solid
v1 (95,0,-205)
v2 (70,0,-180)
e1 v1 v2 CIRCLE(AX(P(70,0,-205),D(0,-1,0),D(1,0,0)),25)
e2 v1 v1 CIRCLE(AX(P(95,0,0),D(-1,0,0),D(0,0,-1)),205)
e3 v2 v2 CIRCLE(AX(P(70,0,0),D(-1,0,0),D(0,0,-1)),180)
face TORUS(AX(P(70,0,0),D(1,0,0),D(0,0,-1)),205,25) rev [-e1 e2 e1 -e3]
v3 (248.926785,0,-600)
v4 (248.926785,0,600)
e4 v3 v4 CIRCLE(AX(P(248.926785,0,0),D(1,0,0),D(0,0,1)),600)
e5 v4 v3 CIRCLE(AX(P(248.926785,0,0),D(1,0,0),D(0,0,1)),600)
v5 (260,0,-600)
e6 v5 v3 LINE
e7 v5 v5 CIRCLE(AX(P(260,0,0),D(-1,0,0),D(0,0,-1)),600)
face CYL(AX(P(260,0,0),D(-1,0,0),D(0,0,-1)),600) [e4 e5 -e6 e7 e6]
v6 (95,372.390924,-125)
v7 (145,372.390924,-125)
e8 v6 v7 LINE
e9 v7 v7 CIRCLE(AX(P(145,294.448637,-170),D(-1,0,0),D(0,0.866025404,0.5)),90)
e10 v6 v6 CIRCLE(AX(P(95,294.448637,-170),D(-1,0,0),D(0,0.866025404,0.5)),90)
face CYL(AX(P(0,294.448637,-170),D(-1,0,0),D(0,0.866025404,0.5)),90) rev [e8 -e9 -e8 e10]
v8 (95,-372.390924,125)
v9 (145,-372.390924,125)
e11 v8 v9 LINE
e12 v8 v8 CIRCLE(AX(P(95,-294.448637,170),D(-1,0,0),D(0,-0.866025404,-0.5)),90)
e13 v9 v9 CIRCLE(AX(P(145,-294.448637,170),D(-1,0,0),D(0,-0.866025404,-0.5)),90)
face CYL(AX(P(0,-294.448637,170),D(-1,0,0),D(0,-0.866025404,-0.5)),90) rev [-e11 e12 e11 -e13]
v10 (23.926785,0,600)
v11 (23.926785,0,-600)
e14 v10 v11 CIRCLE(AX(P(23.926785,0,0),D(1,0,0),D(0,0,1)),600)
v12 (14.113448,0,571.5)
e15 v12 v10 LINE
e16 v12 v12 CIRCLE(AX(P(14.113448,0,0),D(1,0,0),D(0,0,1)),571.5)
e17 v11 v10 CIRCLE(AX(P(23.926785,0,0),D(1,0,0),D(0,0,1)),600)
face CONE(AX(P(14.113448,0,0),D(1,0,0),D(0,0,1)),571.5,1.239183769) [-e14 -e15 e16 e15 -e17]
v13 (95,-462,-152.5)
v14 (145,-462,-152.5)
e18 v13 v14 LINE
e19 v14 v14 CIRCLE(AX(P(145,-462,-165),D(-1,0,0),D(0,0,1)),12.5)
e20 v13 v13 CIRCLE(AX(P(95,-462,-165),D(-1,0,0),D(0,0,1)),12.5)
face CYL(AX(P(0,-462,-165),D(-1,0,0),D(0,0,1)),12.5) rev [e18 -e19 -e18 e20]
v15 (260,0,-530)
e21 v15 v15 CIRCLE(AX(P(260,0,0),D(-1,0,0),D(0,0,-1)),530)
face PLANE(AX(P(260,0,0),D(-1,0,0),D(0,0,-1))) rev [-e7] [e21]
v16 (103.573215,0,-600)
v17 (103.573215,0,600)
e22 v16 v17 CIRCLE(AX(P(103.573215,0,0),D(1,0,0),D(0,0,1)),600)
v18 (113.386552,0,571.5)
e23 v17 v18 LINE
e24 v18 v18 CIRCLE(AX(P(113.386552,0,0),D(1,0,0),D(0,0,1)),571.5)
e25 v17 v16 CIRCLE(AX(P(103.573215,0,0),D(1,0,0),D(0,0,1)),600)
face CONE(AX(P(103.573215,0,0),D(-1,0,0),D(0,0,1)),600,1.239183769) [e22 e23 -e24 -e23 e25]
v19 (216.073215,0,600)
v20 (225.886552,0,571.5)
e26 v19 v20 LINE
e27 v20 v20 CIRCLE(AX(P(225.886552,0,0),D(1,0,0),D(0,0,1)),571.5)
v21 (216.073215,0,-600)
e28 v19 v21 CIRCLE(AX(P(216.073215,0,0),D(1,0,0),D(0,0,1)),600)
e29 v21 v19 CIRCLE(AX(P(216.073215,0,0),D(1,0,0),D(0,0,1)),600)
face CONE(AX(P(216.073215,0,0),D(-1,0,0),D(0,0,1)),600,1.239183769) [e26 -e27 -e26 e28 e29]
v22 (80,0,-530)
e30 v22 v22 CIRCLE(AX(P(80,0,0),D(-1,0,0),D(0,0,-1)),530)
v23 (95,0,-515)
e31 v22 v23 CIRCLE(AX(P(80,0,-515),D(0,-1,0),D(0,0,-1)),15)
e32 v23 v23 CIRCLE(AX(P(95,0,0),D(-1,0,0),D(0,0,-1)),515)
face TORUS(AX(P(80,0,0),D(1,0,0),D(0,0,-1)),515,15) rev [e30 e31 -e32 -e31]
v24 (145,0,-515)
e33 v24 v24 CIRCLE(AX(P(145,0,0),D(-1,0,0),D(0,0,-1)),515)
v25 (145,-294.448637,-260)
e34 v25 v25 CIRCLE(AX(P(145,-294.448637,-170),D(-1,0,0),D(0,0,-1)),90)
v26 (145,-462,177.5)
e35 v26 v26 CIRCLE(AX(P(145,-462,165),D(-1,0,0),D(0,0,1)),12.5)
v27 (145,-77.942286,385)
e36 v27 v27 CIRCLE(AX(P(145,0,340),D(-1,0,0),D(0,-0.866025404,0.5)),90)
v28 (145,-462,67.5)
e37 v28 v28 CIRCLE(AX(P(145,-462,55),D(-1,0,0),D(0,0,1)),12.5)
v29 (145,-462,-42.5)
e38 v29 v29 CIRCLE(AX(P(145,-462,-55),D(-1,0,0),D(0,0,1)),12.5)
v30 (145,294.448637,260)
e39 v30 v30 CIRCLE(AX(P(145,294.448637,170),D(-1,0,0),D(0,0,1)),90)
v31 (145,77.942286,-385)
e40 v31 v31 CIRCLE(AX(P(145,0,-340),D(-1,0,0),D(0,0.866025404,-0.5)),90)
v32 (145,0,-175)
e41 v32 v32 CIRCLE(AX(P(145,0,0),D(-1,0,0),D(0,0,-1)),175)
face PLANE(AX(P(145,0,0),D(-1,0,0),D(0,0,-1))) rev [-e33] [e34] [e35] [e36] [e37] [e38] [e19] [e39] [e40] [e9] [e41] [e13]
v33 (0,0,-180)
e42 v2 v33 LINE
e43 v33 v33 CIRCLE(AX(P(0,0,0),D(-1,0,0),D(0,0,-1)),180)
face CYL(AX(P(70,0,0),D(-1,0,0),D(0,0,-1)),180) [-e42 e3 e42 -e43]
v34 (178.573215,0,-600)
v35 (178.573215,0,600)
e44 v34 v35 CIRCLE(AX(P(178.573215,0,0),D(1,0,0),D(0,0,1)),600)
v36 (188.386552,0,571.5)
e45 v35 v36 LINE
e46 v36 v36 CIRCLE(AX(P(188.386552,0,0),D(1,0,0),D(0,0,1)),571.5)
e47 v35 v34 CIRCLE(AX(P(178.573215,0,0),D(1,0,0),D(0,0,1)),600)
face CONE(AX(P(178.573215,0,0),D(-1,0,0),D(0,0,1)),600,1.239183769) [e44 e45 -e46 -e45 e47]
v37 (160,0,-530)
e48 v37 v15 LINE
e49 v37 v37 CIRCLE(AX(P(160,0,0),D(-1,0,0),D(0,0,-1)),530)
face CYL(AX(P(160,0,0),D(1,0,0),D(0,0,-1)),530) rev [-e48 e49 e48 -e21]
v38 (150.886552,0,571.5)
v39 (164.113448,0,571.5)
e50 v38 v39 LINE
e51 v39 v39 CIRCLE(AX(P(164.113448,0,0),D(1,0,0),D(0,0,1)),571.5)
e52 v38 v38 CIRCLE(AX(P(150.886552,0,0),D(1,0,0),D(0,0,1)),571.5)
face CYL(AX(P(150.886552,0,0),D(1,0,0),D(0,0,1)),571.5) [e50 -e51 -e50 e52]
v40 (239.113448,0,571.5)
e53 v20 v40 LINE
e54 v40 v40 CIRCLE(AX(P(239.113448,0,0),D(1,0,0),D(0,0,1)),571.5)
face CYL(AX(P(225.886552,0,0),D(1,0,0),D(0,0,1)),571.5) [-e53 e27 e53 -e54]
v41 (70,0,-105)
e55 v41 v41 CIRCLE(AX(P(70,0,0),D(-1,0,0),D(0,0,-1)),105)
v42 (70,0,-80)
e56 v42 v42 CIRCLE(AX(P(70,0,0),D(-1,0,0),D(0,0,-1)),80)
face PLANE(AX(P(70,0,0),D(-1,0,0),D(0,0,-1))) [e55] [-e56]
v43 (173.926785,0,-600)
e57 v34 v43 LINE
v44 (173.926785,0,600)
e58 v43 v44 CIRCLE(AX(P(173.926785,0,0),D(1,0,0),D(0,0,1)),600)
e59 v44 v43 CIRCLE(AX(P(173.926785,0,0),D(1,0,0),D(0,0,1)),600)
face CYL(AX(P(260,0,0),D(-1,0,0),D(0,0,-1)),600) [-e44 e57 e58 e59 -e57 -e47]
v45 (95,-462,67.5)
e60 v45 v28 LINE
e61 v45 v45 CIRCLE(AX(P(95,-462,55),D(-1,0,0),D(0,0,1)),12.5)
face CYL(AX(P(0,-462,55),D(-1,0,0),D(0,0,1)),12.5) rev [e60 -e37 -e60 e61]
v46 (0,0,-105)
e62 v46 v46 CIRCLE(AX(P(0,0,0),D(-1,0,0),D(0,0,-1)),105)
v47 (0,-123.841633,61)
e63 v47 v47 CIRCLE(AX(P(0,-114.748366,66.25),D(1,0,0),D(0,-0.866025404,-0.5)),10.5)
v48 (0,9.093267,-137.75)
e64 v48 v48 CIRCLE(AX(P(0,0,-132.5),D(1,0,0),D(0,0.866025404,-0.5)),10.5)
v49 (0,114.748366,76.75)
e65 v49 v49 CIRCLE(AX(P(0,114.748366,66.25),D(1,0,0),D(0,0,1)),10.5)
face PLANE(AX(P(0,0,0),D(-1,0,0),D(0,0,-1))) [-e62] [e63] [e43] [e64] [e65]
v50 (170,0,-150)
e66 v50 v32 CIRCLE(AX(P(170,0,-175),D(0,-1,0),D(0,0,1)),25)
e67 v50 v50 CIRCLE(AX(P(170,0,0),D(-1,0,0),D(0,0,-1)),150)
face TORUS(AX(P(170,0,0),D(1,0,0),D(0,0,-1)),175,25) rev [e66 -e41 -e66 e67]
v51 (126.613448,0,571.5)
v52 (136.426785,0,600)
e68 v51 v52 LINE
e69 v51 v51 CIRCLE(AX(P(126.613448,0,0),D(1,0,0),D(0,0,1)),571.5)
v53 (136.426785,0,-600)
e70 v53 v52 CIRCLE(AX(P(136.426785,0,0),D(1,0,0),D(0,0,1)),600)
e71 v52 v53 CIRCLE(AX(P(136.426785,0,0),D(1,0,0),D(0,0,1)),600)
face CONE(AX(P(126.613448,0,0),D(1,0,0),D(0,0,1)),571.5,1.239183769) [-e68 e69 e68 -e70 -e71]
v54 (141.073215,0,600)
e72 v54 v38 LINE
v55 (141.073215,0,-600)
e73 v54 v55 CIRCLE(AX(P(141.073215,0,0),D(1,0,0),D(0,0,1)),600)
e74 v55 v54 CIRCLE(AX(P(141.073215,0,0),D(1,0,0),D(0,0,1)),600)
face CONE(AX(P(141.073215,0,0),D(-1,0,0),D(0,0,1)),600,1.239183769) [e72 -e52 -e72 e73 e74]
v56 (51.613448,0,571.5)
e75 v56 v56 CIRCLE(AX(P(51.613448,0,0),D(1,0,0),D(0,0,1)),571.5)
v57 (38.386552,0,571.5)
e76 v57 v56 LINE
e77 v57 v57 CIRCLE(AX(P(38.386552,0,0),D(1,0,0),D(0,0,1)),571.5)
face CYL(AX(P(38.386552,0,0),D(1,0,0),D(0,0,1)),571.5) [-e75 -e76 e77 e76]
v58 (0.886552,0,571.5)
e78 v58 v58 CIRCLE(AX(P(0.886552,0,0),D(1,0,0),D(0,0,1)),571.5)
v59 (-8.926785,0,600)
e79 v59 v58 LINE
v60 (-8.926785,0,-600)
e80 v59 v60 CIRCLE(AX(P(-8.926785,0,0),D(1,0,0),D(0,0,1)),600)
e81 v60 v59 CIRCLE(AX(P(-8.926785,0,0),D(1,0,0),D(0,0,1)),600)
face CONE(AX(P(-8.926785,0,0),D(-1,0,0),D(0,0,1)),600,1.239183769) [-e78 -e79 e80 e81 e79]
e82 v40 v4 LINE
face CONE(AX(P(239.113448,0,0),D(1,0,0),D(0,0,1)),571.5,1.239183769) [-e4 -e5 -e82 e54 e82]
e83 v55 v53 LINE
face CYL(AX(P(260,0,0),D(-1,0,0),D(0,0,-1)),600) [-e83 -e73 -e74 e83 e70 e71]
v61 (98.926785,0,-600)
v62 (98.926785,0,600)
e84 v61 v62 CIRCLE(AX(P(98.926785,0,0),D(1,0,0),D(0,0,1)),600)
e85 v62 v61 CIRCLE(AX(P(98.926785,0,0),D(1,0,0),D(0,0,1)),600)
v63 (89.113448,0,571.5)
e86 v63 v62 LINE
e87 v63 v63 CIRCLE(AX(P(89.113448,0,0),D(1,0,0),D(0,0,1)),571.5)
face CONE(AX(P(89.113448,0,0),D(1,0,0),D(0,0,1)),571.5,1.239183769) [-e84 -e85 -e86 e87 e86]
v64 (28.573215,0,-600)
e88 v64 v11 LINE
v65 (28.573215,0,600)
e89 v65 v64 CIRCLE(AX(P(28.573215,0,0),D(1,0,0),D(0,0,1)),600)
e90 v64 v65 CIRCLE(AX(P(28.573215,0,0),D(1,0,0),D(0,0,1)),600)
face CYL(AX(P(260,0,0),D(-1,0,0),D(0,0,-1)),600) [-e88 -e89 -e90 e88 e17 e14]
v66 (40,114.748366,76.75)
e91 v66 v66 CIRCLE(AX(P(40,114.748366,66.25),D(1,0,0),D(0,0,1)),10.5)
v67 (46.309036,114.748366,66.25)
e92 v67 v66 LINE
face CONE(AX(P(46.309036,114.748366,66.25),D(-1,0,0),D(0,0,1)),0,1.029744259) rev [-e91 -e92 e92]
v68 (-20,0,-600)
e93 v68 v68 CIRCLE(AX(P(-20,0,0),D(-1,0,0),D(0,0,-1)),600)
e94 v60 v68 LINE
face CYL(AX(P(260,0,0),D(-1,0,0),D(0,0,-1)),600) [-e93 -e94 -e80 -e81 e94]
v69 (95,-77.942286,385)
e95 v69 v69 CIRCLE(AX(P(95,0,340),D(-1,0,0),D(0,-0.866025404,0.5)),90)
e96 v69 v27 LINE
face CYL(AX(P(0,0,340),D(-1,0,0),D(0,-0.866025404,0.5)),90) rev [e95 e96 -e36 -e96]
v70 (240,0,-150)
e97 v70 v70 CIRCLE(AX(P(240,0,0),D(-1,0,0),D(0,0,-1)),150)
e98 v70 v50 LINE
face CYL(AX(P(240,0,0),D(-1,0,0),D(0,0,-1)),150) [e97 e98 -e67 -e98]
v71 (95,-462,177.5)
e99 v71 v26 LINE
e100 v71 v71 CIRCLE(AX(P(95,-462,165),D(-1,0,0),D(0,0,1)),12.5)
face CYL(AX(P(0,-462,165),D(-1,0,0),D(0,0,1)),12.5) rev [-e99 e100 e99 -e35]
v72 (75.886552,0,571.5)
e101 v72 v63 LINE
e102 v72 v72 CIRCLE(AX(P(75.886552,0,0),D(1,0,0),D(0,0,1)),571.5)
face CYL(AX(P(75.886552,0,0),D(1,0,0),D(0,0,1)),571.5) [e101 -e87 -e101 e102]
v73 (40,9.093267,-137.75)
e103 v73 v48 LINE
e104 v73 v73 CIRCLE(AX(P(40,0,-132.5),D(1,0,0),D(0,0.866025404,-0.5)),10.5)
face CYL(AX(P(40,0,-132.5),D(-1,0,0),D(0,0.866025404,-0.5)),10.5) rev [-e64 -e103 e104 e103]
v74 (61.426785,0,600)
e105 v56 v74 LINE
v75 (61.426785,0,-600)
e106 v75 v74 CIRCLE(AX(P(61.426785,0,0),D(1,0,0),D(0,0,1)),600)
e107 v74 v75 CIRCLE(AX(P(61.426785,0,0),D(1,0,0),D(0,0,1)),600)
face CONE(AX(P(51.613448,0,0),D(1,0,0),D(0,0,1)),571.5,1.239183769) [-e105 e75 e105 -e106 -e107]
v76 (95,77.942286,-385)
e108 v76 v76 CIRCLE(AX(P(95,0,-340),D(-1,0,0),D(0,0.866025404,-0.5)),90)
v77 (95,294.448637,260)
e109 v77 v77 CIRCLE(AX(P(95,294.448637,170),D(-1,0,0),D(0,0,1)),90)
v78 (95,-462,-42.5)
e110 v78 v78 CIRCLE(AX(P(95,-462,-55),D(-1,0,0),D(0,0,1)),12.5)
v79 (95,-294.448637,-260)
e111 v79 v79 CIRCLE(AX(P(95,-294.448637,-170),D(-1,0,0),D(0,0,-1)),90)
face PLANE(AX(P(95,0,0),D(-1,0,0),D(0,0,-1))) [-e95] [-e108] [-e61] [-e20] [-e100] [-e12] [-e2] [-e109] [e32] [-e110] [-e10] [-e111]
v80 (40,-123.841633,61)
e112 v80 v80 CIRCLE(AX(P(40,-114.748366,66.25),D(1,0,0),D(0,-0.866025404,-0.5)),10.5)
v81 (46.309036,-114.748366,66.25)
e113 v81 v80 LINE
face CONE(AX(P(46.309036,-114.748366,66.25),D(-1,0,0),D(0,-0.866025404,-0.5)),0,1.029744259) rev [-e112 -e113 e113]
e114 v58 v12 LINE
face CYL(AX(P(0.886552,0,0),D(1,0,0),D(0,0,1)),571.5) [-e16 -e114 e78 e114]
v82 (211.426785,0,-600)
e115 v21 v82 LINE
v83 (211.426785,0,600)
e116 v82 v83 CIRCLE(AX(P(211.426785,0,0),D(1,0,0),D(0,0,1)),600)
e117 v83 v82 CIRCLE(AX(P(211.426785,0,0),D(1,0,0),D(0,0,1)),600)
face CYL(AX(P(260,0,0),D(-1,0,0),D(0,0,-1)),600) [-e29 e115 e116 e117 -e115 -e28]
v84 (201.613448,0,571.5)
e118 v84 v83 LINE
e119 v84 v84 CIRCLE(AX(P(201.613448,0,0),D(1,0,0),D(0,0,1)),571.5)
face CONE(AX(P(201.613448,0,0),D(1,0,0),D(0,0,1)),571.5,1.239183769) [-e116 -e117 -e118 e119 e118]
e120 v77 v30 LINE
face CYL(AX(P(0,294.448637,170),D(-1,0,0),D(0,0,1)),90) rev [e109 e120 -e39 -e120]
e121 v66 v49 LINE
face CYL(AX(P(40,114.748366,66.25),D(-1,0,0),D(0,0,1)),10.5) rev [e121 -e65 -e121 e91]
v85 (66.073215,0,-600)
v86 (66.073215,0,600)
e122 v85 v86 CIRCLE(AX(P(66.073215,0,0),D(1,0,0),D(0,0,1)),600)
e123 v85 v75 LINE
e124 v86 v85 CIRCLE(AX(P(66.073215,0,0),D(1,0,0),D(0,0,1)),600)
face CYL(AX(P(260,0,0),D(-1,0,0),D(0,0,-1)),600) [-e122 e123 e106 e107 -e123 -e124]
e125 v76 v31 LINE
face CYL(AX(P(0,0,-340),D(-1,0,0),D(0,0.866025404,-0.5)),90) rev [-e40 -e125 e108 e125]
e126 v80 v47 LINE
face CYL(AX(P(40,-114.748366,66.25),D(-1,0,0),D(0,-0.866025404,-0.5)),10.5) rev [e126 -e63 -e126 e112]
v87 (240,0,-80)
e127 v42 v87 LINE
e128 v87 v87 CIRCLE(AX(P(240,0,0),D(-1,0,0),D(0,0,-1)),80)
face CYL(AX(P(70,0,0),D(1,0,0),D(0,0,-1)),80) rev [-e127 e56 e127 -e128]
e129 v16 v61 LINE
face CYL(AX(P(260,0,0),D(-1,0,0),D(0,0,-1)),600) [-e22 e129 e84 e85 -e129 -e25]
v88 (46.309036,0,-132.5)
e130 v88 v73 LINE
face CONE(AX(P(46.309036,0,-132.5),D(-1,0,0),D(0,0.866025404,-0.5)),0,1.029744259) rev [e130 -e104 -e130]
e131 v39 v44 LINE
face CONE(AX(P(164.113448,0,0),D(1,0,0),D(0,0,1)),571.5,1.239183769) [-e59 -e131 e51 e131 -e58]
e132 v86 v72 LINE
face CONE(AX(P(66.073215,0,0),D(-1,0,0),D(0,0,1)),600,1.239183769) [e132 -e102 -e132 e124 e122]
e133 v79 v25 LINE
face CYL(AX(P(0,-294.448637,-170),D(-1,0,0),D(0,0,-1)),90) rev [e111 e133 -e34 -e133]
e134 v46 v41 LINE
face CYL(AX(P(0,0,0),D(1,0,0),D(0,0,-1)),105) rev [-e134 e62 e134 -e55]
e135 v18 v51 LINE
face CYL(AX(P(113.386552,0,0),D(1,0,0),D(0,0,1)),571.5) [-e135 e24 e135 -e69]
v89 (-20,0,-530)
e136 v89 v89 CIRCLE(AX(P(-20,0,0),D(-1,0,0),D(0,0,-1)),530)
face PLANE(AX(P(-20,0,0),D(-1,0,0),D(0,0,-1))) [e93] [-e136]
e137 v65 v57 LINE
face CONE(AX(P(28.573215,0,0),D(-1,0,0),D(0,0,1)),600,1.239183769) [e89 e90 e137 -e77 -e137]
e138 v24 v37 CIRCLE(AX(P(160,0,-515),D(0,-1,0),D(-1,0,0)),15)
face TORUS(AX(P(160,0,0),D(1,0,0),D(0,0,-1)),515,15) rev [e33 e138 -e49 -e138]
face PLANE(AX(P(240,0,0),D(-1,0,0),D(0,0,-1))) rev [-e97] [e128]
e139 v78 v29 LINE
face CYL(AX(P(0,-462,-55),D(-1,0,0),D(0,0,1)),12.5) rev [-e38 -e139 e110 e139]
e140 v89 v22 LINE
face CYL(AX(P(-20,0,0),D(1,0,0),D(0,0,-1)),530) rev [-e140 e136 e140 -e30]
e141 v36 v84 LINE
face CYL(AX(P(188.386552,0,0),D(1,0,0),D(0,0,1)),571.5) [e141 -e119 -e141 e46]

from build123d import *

# Parameters (mm, degrees)
SKETCH4_R          = 90
CUT_EXTRUDE1_DEPTH = 343
CIRPATTERN1_COUNT  = 6
CIRPATTERN2_COUNT  = 3
SKETCH8_R          = 12.5
CUT_EXTRUDE3_DEPTH = 238
LPATTERN1_COUNT    = 7
LPATTERN1_PITCH    = 37.5


with BuildPart() as part:
    # Sketch2 → Revolve1 (revolve)
    with BuildSketch(Plane.XY, mode=Mode.PRIVATE) as revolve1_sk:
        with BuildLine():
            Line((-20, 600), (-20, 530))
            Line((-20, 530), (80, 530))
            ThreePointArc((80, 530), (90.606601718, 525.606601718), (95, 515))
            Line((95, 515), (95, 205))
            ThreePointArc((95, 205), (87.67766953, 187.32233047), (70, 180))
            Line((70, 180), (0, 180))
            Line((0, 180), (0, 105))
            Line((0, 105), (70, 105))
            Line((70, 105), (70, 80))
            Line((70, 80), (240, 80))
            Line((240, 80), (240, 150))
            Line((240, 150), (170, 150))
            ThreePointArc((170, 150), (152.32233047, 157.32233047), (145, 175))
            Line((145, 175), (145, 515))
            ThreePointArc((145, 515), (149.393398282, 525.606601718), (160, 530))
            Line((160, 530), (260, 530))
            Line((260, 530), (260, 600))
            Line((260, 600), (-20, 600))
        make_face()
    revolve(revolve1_sk.sketch.rotate(Axis((225.657059372, 0, 0), (-1, 0, 0)), 90), axis=Axis((225.657059372, 0, 0), (-1, 0, 0)))

    # Sketch4 → Cut-Extrude1 (cut)
    with BuildSketch(Plane(origin=(0, 0, 0), x_dir=(0, 0, -1), z_dir=(1, 0, 0))):
        with Locations(Location((-170, 294.448637287, 0), (0, 0, 180))):
            Circle(SKETCH4_R)
    cut_extrude1 = extrude(amount=CUT_EXTRUDE1_DEPTH, mode=Mode.SUBTRACT)

    # CirPattern1: Cut-Extrude1 ×6 about axis
    cirpattern1_axis = Axis((0, 0, 0), (1, 0, 0))
    for i in range(1, CIRPATTERN1_COUNT):
        add(cut_extrude1.rotate(cirpattern1_axis, i * 360 / CIRPATTERN1_COUNT), mode=Mode.SUBTRACT)

    # Sketch6 → M24 Tapped Hole1 (revolve, cut)
    with BuildSketch(Plane(origin=(0, 114.748366001, 66.25), x_dir=(0, 0, 1), z_dir=(0, 1, 0))):
        Polygon((0, 0), (0, 46.3090365), (10.5, 40), (10.5, 0), align=None)
    m24_tapped_hole1 = revolve(axis=Axis((-6.35, 114.748366001, 66.25), (1, 0, 0)), mode=Mode.SUBTRACT)

    # CirPattern2: M24 Tapped Hole1 ×3 about axis
    cirpattern2_axis = Axis((0, 0, 0), (1, 0, 0))
    for i in range(1, CIRPATTERN2_COUNT):
        add(m24_tapped_hole1.rotate(cirpattern2_axis, i * 360 / CIRPATTERN2_COUNT), mode=Mode.SUBTRACT)

    # Sketch8 → Cut-Extrude3 (cut)
    with BuildSketch(Plane(origin=(0, 0, 0), x_dir=(0, 0, -1), z_dir=(1, 0, 0))):
        with Locations(Location((-55, -462, 0), (0, 0, 180))):
            Circle(SKETCH8_R)
        with Locations(Location((-165, -462, 0), (0, 0, 180))):
            Circle(SKETCH8_R)
        with Locations(Location((55, -462, 0), (0, 0, 180))):
            Circle(SKETCH8_R)
        with Locations(Location((165, -462, 0), (0, 0, 180))):
            Circle(SKETCH8_R)
    extrude(amount=CUT_EXTRUDE3_DEPTH, mode=Mode.SUBTRACT)

    # Sketch9 → Cut-Revolve1 (revolve, cut)
    with BuildSketch(Plane.XY, mode=Mode.PRIVATE) as cut_revolve1_sk:
        Polygon((-8.926784713, 600), (0.886552266, 571.5), (14.113447734, 571.5), (23.926784713, 600), align=None)
    cut_revolve1 = revolve(cut_revolve1_sk.sketch.rotate(Axis((0, 0, 0), (1, 0, 0)), 90), axis=Axis((0, 0, 0), (1, 0, 0)), mode=Mode.SUBTRACT)

    # LPattern1: Cut-Revolve1 ×7
    with Locations(*[(i * LPATTERN1_PITCH, 0, 0) for i in range(1, LPATTERN1_COUNT)]):
        add(cut_revolve1, mode=Mode.SUBTRACT)


solid = part.part
